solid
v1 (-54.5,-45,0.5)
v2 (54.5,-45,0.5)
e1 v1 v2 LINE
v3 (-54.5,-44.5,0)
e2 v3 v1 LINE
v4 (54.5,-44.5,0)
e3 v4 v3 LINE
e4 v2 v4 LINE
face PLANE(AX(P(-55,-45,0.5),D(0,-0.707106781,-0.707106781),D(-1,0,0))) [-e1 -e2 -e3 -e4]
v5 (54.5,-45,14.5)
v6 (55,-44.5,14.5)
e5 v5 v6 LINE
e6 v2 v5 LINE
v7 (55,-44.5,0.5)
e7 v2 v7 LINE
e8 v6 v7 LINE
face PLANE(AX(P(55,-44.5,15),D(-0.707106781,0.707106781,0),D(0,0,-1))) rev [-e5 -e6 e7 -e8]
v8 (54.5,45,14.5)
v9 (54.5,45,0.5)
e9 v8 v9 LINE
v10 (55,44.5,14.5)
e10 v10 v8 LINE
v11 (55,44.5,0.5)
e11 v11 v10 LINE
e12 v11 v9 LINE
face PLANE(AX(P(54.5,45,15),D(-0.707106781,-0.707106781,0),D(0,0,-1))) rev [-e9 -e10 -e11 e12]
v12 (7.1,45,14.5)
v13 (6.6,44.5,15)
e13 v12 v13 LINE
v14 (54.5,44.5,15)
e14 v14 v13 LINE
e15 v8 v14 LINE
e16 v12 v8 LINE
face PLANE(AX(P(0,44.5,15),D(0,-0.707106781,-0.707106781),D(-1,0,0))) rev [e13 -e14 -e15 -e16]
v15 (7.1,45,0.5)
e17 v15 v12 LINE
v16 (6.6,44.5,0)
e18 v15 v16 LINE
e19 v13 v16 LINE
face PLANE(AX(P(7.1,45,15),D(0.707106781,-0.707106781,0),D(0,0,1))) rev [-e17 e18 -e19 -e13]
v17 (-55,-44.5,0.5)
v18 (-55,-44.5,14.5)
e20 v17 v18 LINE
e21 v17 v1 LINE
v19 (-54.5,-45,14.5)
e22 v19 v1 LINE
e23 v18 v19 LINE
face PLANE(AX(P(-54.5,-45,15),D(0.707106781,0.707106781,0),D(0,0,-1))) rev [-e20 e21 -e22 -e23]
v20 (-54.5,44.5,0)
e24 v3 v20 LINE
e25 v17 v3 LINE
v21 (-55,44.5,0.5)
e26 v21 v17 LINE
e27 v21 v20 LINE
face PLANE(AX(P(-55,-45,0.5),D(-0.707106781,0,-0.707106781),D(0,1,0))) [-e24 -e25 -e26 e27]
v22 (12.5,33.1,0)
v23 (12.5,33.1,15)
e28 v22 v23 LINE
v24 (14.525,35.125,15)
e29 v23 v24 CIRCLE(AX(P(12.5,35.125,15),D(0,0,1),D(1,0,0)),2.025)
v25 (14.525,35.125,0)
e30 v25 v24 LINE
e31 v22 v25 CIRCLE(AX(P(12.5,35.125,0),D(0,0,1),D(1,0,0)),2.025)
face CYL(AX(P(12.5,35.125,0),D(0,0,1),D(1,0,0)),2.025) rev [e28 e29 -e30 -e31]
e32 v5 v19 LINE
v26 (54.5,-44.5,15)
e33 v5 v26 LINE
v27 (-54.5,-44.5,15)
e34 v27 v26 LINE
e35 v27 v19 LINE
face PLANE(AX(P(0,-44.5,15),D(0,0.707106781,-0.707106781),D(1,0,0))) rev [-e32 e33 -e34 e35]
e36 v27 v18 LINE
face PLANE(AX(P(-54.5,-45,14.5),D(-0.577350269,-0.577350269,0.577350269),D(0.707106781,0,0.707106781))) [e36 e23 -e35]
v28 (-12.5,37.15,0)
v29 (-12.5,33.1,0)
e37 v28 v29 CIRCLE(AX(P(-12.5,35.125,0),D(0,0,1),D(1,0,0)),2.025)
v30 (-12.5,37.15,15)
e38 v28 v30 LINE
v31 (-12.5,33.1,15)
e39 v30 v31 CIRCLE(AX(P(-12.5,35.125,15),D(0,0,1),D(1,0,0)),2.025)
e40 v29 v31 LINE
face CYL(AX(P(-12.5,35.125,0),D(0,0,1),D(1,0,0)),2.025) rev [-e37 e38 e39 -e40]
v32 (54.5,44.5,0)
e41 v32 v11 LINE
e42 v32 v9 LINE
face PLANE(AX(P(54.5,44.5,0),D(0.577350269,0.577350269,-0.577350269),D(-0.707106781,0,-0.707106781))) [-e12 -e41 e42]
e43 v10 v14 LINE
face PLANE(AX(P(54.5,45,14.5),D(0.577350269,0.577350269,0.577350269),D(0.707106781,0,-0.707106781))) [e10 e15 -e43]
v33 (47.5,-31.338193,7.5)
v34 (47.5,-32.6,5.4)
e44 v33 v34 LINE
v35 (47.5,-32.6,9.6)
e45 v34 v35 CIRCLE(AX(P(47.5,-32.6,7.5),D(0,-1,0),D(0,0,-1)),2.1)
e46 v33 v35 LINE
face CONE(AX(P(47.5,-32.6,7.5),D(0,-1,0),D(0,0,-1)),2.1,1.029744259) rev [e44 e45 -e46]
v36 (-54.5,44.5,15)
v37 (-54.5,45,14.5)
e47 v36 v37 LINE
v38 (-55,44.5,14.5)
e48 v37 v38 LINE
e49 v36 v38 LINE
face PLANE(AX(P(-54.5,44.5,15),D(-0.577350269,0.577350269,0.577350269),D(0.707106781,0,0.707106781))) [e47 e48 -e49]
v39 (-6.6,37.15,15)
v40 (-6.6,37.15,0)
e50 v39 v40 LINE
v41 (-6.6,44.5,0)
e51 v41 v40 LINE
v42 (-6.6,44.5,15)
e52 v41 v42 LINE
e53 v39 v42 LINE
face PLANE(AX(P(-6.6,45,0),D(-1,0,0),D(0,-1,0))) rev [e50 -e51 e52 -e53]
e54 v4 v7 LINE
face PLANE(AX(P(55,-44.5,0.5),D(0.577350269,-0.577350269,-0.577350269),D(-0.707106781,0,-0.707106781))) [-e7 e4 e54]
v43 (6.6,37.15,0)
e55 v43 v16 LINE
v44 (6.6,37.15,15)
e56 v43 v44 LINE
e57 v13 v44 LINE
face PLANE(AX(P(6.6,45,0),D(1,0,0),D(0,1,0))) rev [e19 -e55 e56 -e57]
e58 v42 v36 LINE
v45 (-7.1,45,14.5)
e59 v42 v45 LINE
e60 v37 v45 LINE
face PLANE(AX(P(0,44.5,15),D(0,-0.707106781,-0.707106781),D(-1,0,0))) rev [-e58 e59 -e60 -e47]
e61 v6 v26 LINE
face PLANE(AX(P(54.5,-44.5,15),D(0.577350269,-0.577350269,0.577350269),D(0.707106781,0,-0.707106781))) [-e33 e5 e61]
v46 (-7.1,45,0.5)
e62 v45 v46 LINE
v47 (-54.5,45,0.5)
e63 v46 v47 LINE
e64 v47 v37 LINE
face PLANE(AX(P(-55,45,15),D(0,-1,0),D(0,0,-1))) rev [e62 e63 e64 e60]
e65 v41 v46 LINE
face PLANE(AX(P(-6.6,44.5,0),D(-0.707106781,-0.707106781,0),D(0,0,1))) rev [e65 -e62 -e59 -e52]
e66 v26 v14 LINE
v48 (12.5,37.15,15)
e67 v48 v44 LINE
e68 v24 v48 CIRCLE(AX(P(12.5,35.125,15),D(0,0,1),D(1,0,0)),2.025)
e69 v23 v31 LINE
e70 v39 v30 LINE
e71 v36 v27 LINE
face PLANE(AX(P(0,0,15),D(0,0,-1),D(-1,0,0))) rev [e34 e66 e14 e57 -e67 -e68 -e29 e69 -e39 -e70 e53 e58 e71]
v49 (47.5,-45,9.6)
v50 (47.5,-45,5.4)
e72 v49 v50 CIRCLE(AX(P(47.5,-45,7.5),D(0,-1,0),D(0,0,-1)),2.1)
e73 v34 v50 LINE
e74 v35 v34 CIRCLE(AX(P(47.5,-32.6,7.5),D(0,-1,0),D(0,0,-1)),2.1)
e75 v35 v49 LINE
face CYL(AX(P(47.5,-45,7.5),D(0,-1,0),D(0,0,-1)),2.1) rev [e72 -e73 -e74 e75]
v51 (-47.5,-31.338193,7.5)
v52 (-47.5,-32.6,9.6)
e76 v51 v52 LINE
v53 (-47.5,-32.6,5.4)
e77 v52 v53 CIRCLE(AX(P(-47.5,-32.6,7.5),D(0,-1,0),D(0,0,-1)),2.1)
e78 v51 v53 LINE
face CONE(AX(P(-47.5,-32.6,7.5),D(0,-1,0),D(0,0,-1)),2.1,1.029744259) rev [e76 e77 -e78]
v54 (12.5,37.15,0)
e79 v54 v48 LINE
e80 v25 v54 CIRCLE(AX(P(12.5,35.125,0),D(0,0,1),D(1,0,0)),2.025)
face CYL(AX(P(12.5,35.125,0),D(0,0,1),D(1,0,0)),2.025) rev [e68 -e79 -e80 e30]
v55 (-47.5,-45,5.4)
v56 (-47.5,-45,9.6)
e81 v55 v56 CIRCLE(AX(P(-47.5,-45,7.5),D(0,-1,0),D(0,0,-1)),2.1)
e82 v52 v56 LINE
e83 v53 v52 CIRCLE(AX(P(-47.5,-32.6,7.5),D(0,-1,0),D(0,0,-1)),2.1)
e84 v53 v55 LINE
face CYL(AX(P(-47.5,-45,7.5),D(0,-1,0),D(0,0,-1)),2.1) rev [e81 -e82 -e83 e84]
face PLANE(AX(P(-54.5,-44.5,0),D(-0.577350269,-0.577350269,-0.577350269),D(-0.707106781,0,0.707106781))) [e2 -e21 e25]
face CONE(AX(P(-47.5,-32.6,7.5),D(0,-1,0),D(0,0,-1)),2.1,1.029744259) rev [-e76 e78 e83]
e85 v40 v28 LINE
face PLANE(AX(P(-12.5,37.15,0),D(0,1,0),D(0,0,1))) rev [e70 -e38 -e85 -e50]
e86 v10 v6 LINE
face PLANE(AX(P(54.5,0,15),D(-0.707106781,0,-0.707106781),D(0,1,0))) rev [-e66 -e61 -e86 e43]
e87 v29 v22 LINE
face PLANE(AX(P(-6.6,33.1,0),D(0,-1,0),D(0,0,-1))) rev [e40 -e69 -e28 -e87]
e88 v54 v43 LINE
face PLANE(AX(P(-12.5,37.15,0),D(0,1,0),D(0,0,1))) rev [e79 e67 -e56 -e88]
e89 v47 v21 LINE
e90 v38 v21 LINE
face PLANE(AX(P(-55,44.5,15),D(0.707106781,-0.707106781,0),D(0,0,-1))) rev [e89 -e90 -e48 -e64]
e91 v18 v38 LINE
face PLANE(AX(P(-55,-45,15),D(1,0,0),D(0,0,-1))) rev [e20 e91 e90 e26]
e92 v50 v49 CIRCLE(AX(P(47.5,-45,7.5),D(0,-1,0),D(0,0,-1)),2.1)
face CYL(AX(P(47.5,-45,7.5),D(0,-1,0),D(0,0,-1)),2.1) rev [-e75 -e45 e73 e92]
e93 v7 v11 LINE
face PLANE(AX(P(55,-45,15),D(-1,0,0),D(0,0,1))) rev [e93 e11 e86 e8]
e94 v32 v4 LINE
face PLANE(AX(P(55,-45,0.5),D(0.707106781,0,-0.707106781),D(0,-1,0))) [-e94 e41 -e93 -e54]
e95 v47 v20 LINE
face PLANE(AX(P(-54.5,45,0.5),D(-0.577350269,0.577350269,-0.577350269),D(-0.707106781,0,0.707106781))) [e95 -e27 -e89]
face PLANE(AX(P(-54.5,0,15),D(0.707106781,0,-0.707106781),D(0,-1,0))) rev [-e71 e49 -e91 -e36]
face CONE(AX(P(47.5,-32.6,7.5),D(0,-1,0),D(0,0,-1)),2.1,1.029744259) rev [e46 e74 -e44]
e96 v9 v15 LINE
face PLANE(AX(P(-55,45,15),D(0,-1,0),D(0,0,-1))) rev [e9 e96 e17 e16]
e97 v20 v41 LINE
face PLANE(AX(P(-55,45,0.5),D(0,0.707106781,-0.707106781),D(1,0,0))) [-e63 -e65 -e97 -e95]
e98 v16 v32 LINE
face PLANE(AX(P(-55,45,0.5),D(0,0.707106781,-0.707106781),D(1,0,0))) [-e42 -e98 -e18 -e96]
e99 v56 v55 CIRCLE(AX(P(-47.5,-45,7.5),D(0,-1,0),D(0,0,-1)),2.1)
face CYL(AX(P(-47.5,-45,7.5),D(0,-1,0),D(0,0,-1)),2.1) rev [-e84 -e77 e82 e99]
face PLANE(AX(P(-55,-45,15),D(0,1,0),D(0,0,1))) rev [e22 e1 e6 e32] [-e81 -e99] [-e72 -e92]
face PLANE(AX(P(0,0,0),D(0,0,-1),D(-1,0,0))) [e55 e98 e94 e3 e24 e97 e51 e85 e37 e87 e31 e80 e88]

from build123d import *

# Parameters (mm, degrees)
SKETCH_1_W               = 110
SKETCH_1_H               = 90
EXTRUDE_1_DEPTH          = 15
CUT_EXTRUDE_1_DEPTH      = 73.629195232
CUT_EXTRUDE_1_DEPTH_BACK = 73.629195232
SKETCH_2_W               = 13.2
SKETCH_2_H               = 11.9
CUT_EXTRUDE_2_DEPTH      = 73.629195232
HOLE_WIZARD_M5_1_D       = 4.2
HOLE_WIZARD_M5_1_DEPTH   = 12.4
HOLE_WIZARD_M5_1_TIP     = 1.2618073
CHAMFER_1_SIZE           = 0.5


with BuildPart() as part:
    # 草图1 → 凸台-拉伸1 (new body)
    with BuildSketch(Plane.XY):
        Rectangle(SKETCH_1_W, SKETCH_1_H)
    extrude(amount=EXTRUDE_1_DEPTH)

    # 草图2 → 切除-拉伸1 (cut, two sides: drawn at the far end of the back side and taken through both)
    with BuildSketch(Plane.XY.offset(15).offset(-CUT_EXTRUDE_1_DEPTH_BACK)):
        with Locations((0, 39.05)):
            Rectangle(SKETCH_2_W, SKETCH_2_H)
    extrude(amount=CUT_EXTRUDE_1_DEPTH + CUT_EXTRUDE_1_DEPTH_BACK, mode=Mode.SUBTRACT)

    # 草图3 → 切除-拉伸2 (cut, through all)
    with BuildSketch(Plane.XY.offset(15)):
        with BuildLine():
            Line((-12.5, 37.15), (12.5, 37.15))
            ThreePointArc((12.5, 37.15), (14.525, 35.125), (12.5, 33.1))
            Line((12.5, 33.1), (-12.5, 33.1))
            ThreePointArc((-12.5, 33.1), (-14.525, 35.125), (-12.5, 37.15))
        make_face()
    extrude(amount=-CUT_EXTRUDE_2_DEPTH, mode=Mode.SUBTRACT)

    # M5 螺纹孔1
    with Locations(Plane(origin=(0, -45, 0), x_dir=(-1, 0, 0), z_dir=(0, -1, 0))):
        with Locations((-47.5, -7.5), (47.5, -7.5)):
            Hole(HOLE_WIZARD_M5_1_D / 2, depth=HOLE_WIZARD_M5_1_DEPTH)
            with Locations((0, 0, -(HOLE_WIZARD_M5_1_DEPTH + HOLE_WIZARD_M5_1_TIP / 2))):  # 118° drill point
                Cone(0, HOLE_WIZARD_M5_1_D / 2, HOLE_WIZARD_M5_1_TIP, mode=Mode.SUBTRACT)

    # 倒角1
    chamfer_1_edges = [part.edges().sort_by_distance(p)[0] for p in [
        (-55, 0, 15),
        (-30.8, 45, 0),
        (-30.8, 45, 15),
        (0, -45, 15),
        (-6.6, 45, 7.5),
        (6.6, 45, 7.5),
        (55, 0, 15),
        (0, -45, 0),
        (-55, 0, 0),
        (30.8, 45, 0),
        (55, 0, 0),
        (55, -45, 7.5),
        (-55, -45, 7.5),
        (-55, 45, 7.5),
        (55, 45, 7.5),
        (30.8, 45, 15),
    ]]
    chamfer(chamfer_1_edges, length=CHAMFER_1_SIZE)


solid = part.part
